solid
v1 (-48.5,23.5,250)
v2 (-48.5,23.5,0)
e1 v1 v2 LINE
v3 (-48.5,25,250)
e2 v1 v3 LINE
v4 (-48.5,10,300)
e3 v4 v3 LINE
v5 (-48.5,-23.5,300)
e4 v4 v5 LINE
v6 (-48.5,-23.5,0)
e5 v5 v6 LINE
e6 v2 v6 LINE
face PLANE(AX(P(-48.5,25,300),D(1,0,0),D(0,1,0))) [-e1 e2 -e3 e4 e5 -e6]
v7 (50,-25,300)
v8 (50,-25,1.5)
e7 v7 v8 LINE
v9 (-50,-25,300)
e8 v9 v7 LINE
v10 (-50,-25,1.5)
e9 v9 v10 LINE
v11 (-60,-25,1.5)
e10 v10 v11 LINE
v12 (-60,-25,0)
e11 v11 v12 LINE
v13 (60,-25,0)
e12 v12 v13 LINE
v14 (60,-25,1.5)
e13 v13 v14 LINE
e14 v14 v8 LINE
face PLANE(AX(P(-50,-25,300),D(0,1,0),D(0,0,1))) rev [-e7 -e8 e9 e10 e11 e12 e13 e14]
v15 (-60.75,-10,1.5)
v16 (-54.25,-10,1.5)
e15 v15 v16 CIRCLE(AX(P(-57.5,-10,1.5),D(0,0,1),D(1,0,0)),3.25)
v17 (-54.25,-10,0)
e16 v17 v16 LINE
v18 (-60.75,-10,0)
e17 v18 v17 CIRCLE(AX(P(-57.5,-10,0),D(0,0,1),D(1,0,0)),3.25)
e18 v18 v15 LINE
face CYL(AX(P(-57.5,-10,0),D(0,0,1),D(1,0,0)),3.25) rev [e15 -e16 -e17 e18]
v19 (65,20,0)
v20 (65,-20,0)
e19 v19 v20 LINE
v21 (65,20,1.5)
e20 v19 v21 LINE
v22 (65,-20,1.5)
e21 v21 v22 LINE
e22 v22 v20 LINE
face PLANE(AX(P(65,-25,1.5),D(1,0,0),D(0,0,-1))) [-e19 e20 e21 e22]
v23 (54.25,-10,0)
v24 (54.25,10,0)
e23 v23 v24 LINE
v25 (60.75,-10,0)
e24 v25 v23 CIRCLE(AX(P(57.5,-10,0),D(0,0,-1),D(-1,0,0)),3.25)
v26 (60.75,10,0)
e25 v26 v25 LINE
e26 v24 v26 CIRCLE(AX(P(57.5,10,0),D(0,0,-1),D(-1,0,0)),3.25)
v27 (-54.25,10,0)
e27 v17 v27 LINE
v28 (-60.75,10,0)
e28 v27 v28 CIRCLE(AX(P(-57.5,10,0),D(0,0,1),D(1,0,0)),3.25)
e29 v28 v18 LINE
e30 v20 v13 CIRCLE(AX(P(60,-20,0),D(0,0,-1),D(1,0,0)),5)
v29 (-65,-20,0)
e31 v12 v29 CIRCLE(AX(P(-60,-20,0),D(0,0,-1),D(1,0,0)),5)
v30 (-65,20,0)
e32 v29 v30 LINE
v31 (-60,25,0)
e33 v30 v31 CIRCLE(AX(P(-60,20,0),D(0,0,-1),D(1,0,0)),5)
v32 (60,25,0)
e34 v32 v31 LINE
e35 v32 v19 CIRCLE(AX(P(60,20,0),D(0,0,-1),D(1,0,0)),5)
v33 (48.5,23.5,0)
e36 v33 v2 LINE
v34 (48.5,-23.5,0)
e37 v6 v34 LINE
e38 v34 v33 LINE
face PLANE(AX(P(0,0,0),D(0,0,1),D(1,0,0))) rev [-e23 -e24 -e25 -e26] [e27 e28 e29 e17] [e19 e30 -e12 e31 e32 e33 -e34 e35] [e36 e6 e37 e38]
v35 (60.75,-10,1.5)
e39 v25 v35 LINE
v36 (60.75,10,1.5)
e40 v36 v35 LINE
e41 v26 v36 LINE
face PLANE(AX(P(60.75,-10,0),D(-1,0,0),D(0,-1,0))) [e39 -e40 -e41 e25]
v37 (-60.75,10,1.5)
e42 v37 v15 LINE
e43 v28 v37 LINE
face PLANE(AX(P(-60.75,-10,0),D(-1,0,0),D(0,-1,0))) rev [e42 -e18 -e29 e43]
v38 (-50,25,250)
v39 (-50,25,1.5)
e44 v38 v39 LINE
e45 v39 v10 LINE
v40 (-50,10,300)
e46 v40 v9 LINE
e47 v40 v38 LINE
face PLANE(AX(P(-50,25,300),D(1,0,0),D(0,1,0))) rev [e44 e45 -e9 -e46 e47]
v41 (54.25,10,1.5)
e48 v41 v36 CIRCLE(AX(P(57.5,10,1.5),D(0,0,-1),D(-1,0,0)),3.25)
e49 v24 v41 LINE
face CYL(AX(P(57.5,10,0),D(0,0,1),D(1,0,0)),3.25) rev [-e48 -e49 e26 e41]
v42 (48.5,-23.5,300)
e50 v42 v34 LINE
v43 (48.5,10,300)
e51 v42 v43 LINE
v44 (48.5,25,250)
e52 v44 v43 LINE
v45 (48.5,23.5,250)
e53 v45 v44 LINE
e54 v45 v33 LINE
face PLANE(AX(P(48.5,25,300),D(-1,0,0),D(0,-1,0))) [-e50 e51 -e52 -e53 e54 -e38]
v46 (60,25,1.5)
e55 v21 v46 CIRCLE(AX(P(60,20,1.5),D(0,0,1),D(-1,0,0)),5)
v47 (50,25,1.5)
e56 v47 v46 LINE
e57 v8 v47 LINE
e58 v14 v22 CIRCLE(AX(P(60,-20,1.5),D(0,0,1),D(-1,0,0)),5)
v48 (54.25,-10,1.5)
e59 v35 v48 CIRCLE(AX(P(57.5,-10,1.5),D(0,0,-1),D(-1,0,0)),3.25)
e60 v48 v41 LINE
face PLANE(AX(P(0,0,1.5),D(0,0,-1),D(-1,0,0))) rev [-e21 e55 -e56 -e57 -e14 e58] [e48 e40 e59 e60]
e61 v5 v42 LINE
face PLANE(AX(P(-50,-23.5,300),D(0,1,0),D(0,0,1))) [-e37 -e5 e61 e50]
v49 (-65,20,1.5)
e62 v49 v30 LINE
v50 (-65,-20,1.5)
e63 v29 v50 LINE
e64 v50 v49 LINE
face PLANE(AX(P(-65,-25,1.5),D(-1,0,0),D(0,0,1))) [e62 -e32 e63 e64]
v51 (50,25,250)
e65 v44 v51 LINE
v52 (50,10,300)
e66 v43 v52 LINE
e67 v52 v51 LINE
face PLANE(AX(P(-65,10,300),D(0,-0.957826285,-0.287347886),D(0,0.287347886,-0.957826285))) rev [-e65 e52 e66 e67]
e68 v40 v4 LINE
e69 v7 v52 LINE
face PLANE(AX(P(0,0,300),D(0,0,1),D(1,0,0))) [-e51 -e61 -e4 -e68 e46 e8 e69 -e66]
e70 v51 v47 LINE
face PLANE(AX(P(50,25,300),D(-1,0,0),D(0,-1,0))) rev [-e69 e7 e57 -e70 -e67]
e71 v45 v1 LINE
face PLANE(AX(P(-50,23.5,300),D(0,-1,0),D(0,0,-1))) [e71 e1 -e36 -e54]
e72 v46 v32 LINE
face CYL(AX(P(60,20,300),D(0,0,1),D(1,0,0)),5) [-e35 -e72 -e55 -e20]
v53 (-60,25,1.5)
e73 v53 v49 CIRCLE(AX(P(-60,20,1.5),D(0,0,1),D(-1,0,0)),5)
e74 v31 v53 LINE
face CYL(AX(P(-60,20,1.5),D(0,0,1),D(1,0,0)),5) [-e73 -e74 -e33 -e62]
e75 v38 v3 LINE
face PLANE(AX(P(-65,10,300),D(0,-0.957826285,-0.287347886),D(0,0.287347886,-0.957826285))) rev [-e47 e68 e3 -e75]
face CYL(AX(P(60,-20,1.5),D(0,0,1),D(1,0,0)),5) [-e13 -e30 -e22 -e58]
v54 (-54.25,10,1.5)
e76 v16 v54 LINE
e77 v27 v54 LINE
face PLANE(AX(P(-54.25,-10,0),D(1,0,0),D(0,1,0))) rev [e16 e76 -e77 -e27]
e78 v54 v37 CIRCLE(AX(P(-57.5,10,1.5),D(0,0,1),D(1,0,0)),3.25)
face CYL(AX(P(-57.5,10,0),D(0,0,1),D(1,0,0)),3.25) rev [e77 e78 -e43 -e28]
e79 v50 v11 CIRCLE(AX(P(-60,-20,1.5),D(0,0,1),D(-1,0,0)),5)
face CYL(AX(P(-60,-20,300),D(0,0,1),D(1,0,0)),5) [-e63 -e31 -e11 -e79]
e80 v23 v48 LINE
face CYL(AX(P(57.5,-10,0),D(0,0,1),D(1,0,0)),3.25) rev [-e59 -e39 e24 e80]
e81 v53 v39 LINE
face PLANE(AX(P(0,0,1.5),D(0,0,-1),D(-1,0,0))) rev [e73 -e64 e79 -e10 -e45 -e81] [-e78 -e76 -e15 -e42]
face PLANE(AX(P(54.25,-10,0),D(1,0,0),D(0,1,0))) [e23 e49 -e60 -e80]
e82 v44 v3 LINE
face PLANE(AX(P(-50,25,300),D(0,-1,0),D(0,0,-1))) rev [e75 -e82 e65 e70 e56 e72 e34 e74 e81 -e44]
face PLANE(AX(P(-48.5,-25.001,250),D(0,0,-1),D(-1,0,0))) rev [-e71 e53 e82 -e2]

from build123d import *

# Parameters (mm, degrees)
SKETCH_14_W         = 100
SKETCH_14_H         = 50
EXTRUDE_1_DEPTH     = 300
SHELL_1_T           = -1.5
SKETCH_15_W         = 15
SKETCH_15_H         = 50
EXTRUDE_2_DEPTH     = 1.5
CUT_EXTRUDE_1_DEPTH = 323.257660886
FILLET_1_R          = 5
CUT_EXTRUDE_4_DEPTH = 307.51631278
CUT_EXTRUDE_5_REACH = 313.006
SKETCH_21_W         = 97
SKETCH_21_H         = 10


with BuildPart() as part:
    # 草图14 → 凸台-拉伸1 (new body)
    with BuildSketch(Plane.XY):
        Rectangle(SKETCH_14_W, SKETCH_14_H)
    extrude(amount=EXTRUDE_1_DEPTH)

    # 抽壳1
    shell_1_openings = [part.faces().sort_by_distance(p)[0] for p in [
        (0, 0, 300),
        (0, 0, 0),
    ]]
    offset(amount=SHELL_1_T, openings=shell_1_openings, kind=Kind.INTERSECTION)

    # 草图15 → 凸台-拉伸2 (add)
    with BuildSketch(Plane(origin=(0, 0, 0), x_dir=(-1, 0, 0), z_dir=(0, 0, -1))):
        with Locations((-57.5, 0)):
            Rectangle(SKETCH_15_W, SKETCH_15_H)
        with Locations((57.5, 0)):
            Rectangle(SKETCH_15_W, SKETCH_15_H)
    extrude(amount=-EXTRUDE_2_DEPTH)

    # 草图16 → 切除-拉伸1 (cut, through all)
    with BuildSketch(Plane(origin=(50, 0, 0), x_dir=(0, 0, -1), z_dir=(1, 0, 0))):
        Polygon((-300, 10), (-250, 25), (-300, 25), align=None)
    extrude(amount=-CUT_EXTRUDE_1_DEPTH, mode=Mode.SUBTRACT)

    # 圆角1
    fillet_1_edges = [part.edges().sort_by_distance(p)[0] for p in [
        (65, -25, 0.75),
        (65, 25, 0.75),
        (-65, 25, 0.75),
        (-65, -25, 0.75),
    ]]
    fillet(fillet_1_edges, radius=FILLET_1_R)

    # 草图20 → 切除-拉伸4 (cut, through all)
    with BuildSketch(Plane.XY.offset(1.5)):
        with BuildLine():
            Line((-60.75, -10), (-60.75, 10))
            ThreePointArc((-60.75, 10), (-57.5, 13.25), (-54.25, 10))
            Line((-54.25, 10), (-54.25, -10))
            ThreePointArc((-54.25, -10), (-57.5, -13.25), (-60.75, -10))
        make_face()
    cut_extrude_4 = extrude(amount=-CUT_EXTRUDE_4_DEPTH, mode=Mode.SUBTRACT)

    # 镜向1: 切除-拉伸4 across plane
    add(cut_extrude_4.mirror(Plane(origin=(0, 0, 0), x_dir=(0, 0, 1), z_dir=(1, 0, 0))), mode=Mode.SUBTRACT)

    # 草图21 → 切除-拉伸5 (cut, up to next)
    with BuildSketch(Plane(origin=(0, 25, 0), x_dir=(1, 0, 0), z_dir=(0, 1, 0)), mode=Mode.PRIVATE) as cut_extrude_5_sk1:
        with Locations((0, -255)):
            Rectangle(SKETCH_21_W, SKETCH_21_H)
    cut_extrude_5_tool1 = extrude(cut_extrude_5_sk1.sketch, amount=-CUT_EXTRUDE_5_REACH, mode=Mode.PRIVATE) & part.part
    add(cut_extrude_5_tool1.solids().sort_by_distance((0, 25, 255))[0], mode=Mode.SUBTRACT)


solid = part.part
